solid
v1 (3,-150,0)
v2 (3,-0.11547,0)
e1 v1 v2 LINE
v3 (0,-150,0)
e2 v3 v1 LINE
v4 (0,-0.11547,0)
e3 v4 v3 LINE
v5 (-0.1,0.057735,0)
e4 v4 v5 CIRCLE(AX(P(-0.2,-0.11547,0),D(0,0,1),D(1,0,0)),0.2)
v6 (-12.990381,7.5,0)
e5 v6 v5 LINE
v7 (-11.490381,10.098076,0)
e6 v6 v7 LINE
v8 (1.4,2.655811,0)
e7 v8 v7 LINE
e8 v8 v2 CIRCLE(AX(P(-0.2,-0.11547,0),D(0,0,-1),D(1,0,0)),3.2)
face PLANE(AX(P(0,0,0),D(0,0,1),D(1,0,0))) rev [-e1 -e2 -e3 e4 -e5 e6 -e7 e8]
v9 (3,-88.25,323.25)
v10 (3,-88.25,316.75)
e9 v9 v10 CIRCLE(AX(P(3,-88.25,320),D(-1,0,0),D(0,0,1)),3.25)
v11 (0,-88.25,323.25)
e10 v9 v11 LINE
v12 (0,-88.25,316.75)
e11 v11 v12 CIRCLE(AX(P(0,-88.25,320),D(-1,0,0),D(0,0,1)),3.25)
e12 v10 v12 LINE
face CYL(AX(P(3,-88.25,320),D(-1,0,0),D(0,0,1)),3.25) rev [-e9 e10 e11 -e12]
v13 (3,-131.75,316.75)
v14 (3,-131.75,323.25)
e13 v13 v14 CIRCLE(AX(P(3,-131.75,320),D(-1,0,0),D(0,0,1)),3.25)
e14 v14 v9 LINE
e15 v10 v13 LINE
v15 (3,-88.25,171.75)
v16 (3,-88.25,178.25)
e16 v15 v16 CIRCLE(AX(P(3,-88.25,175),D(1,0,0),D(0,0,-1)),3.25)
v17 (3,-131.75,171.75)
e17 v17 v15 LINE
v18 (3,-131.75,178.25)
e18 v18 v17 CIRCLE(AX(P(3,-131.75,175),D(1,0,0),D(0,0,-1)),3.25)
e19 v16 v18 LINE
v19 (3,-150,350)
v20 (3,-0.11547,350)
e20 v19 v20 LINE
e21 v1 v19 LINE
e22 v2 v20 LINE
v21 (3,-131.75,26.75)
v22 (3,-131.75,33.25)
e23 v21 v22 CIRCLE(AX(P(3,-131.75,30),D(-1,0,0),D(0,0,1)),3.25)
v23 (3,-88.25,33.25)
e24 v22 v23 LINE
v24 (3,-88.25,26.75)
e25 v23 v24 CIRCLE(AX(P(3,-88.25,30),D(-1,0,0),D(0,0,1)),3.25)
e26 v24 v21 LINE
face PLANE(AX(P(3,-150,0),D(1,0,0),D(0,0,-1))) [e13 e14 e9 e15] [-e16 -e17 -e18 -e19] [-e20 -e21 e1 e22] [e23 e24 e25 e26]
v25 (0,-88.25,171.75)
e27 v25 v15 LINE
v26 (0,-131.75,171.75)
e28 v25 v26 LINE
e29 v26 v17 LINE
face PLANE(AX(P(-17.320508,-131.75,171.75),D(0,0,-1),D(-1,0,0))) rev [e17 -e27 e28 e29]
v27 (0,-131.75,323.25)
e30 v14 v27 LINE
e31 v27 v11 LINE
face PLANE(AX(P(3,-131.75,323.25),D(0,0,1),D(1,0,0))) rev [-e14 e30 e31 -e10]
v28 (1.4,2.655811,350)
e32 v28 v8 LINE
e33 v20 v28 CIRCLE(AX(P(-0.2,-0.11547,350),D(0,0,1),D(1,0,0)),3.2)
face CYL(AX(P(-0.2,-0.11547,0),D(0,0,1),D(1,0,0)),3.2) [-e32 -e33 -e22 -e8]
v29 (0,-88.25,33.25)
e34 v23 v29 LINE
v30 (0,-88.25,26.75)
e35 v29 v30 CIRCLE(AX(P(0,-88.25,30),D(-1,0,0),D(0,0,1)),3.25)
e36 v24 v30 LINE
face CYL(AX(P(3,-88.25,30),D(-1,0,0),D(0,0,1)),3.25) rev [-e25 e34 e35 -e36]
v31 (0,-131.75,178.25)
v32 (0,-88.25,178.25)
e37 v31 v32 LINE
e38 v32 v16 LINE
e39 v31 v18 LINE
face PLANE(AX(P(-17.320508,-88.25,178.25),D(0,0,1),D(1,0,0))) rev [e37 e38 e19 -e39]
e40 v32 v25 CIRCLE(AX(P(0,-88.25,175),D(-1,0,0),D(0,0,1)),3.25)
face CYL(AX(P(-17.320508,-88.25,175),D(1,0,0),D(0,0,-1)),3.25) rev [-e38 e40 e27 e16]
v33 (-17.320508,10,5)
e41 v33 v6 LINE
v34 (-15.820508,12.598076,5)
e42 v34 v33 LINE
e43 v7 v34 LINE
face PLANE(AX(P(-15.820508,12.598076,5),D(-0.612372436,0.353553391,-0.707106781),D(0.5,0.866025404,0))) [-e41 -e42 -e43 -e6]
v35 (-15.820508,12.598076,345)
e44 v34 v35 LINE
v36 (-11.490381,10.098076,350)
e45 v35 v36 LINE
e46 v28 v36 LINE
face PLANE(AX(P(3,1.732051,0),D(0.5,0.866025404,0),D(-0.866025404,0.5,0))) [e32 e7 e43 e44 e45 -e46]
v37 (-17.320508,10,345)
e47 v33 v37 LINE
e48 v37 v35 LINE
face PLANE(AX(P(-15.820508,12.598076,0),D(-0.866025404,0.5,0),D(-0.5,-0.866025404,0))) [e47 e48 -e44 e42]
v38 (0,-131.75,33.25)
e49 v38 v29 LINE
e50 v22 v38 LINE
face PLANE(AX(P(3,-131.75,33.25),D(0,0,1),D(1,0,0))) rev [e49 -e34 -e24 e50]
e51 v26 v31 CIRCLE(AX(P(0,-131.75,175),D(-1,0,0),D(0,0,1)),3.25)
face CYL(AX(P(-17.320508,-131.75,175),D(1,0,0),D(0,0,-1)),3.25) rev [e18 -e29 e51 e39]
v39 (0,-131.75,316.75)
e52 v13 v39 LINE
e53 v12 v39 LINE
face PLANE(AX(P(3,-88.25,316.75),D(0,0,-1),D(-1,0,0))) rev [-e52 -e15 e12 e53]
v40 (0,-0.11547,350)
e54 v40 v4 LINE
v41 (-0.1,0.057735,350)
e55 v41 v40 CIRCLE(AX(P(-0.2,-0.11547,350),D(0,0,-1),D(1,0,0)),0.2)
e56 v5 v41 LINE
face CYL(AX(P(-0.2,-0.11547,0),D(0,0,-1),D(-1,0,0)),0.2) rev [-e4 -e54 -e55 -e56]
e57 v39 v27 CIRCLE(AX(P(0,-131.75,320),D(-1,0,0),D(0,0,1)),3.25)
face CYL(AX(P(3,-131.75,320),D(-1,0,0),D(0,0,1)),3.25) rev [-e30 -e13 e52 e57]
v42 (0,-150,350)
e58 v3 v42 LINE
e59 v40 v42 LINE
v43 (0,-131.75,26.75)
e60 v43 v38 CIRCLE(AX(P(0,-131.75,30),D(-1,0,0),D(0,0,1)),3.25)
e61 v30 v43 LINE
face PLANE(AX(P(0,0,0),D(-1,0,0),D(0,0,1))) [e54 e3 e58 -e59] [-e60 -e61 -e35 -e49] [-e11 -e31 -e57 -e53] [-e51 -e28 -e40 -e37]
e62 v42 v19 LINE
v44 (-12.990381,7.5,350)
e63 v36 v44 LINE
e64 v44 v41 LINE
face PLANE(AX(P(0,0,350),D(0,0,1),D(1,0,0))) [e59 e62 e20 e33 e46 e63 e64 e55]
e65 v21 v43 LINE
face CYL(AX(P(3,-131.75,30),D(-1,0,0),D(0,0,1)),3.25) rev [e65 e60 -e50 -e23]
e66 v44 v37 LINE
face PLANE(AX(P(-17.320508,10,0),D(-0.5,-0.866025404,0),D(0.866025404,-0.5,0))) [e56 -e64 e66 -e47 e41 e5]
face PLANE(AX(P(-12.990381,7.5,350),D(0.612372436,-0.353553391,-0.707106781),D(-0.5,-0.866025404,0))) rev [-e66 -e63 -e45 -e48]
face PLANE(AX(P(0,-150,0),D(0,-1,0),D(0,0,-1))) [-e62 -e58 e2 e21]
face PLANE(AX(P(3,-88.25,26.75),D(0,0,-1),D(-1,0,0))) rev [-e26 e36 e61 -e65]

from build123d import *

# Parameters (mm, degrees)
EXTRUDE_1_DEPTH     = 350
CUT_EXTRUDE_1_DEPTH = 382.182371051
CUT_EXTRUDE_2_DEPTH = 382.182371051
CUT_EXTRUDE_3_DEPTH = 382.330464359
CHAMFER_1_SIZE      = 5
FILLET_1_R          = 0.2
FILLET_2_R          = 3.2


with BuildPart() as part:
    # 草图1 → 凸台-拉伸1 (new body)
    with BuildSketch(Plane.XY.offset(350)):
        Polygon((3, -150), (3, 1.732050808), (-15.820508076, 12.598076211), (-17.320508076, 10), (0, 0), (0, -150), align=None)
    extrude(amount=-EXTRUDE_1_DEPTH)

    # 草图2 → 切除-拉伸1 (cut, through all)
    with BuildSketch(Plane.ZY):
        with BuildLine():
            Line((316.75, -88.25), (316.75, -131.75))
            ThreePointArc((316.75, -131.75), (320, -135), (323.25, -131.75))
            Line((323.25, -131.75), (323.25, -88.25))
            ThreePointArc((323.25, -88.25), (320, -85), (316.75, -88.25))
        make_face()
    extrude(amount=-CUT_EXTRUDE_1_DEPTH, mode=Mode.SUBTRACT)

    # 草图3 → 切除-拉伸2 (cut, through all)
    with BuildSketch(Plane.ZY):
        with BuildLine():
            Line((26.75, -88.25), (26.75, -131.75))
            ThreePointArc((26.75, -131.75), (30, -135), (33.25, -131.75))
            Line((33.25, -131.75), (33.25, -88.25))
            ThreePointArc((33.25, -88.25), (30, -85), (26.75, -88.25))
        make_face()
    extrude(amount=-CUT_EXTRUDE_2_DEPTH, mode=Mode.SUBTRACT)

    # 草图4 → 切除-拉伸3 (cut, through all)
    with BuildSketch(Plane(origin=(3, 0, 0), x_dir=(0, 0, -1), z_dir=(1, 0, 0))):
        with BuildLine():
            Line((-171.75, -131.75), (-171.75, -88.25))
            ThreePointArc((-171.75, -88.25), (-175, -85), (-178.25, -88.25))
            Line((-178.25, -88.25), (-178.25, -131.75))
            ThreePointArc((-178.25, -131.75), (-175, -135), (-171.75, -131.75))
        make_face()
    extrude(amount=-CUT_EXTRUDE_3_DEPTH, mode=Mode.SUBTRACT)

    # 倒角1
    chamfer_1_edges = [part.edges().sort_by_distance(p)[0] for p in [
        (-16.570508076, 11.299038106, 0),
        (-16.570508076, 11.299038106, 350),
    ]]
    chamfer(chamfer_1_edges, length=CHAMFER_1_SIZE)

    # 圆角1
    fillet_1_edges = [part.edges().sort_by_distance(p)[0] for p in [
        (0, 0, 175),
    ]]
    fillet(fillet_1_edges, radius=FILLET_1_R)

    # 圆角2
    fillet_2_edges = [part.edges().sort_by_distance(p)[0] for p in [
        (3, 1.732050808, 175),
    ]]
    fillet(fillet_2_edges, radius=FILLET_2_R)


solid = part.part
